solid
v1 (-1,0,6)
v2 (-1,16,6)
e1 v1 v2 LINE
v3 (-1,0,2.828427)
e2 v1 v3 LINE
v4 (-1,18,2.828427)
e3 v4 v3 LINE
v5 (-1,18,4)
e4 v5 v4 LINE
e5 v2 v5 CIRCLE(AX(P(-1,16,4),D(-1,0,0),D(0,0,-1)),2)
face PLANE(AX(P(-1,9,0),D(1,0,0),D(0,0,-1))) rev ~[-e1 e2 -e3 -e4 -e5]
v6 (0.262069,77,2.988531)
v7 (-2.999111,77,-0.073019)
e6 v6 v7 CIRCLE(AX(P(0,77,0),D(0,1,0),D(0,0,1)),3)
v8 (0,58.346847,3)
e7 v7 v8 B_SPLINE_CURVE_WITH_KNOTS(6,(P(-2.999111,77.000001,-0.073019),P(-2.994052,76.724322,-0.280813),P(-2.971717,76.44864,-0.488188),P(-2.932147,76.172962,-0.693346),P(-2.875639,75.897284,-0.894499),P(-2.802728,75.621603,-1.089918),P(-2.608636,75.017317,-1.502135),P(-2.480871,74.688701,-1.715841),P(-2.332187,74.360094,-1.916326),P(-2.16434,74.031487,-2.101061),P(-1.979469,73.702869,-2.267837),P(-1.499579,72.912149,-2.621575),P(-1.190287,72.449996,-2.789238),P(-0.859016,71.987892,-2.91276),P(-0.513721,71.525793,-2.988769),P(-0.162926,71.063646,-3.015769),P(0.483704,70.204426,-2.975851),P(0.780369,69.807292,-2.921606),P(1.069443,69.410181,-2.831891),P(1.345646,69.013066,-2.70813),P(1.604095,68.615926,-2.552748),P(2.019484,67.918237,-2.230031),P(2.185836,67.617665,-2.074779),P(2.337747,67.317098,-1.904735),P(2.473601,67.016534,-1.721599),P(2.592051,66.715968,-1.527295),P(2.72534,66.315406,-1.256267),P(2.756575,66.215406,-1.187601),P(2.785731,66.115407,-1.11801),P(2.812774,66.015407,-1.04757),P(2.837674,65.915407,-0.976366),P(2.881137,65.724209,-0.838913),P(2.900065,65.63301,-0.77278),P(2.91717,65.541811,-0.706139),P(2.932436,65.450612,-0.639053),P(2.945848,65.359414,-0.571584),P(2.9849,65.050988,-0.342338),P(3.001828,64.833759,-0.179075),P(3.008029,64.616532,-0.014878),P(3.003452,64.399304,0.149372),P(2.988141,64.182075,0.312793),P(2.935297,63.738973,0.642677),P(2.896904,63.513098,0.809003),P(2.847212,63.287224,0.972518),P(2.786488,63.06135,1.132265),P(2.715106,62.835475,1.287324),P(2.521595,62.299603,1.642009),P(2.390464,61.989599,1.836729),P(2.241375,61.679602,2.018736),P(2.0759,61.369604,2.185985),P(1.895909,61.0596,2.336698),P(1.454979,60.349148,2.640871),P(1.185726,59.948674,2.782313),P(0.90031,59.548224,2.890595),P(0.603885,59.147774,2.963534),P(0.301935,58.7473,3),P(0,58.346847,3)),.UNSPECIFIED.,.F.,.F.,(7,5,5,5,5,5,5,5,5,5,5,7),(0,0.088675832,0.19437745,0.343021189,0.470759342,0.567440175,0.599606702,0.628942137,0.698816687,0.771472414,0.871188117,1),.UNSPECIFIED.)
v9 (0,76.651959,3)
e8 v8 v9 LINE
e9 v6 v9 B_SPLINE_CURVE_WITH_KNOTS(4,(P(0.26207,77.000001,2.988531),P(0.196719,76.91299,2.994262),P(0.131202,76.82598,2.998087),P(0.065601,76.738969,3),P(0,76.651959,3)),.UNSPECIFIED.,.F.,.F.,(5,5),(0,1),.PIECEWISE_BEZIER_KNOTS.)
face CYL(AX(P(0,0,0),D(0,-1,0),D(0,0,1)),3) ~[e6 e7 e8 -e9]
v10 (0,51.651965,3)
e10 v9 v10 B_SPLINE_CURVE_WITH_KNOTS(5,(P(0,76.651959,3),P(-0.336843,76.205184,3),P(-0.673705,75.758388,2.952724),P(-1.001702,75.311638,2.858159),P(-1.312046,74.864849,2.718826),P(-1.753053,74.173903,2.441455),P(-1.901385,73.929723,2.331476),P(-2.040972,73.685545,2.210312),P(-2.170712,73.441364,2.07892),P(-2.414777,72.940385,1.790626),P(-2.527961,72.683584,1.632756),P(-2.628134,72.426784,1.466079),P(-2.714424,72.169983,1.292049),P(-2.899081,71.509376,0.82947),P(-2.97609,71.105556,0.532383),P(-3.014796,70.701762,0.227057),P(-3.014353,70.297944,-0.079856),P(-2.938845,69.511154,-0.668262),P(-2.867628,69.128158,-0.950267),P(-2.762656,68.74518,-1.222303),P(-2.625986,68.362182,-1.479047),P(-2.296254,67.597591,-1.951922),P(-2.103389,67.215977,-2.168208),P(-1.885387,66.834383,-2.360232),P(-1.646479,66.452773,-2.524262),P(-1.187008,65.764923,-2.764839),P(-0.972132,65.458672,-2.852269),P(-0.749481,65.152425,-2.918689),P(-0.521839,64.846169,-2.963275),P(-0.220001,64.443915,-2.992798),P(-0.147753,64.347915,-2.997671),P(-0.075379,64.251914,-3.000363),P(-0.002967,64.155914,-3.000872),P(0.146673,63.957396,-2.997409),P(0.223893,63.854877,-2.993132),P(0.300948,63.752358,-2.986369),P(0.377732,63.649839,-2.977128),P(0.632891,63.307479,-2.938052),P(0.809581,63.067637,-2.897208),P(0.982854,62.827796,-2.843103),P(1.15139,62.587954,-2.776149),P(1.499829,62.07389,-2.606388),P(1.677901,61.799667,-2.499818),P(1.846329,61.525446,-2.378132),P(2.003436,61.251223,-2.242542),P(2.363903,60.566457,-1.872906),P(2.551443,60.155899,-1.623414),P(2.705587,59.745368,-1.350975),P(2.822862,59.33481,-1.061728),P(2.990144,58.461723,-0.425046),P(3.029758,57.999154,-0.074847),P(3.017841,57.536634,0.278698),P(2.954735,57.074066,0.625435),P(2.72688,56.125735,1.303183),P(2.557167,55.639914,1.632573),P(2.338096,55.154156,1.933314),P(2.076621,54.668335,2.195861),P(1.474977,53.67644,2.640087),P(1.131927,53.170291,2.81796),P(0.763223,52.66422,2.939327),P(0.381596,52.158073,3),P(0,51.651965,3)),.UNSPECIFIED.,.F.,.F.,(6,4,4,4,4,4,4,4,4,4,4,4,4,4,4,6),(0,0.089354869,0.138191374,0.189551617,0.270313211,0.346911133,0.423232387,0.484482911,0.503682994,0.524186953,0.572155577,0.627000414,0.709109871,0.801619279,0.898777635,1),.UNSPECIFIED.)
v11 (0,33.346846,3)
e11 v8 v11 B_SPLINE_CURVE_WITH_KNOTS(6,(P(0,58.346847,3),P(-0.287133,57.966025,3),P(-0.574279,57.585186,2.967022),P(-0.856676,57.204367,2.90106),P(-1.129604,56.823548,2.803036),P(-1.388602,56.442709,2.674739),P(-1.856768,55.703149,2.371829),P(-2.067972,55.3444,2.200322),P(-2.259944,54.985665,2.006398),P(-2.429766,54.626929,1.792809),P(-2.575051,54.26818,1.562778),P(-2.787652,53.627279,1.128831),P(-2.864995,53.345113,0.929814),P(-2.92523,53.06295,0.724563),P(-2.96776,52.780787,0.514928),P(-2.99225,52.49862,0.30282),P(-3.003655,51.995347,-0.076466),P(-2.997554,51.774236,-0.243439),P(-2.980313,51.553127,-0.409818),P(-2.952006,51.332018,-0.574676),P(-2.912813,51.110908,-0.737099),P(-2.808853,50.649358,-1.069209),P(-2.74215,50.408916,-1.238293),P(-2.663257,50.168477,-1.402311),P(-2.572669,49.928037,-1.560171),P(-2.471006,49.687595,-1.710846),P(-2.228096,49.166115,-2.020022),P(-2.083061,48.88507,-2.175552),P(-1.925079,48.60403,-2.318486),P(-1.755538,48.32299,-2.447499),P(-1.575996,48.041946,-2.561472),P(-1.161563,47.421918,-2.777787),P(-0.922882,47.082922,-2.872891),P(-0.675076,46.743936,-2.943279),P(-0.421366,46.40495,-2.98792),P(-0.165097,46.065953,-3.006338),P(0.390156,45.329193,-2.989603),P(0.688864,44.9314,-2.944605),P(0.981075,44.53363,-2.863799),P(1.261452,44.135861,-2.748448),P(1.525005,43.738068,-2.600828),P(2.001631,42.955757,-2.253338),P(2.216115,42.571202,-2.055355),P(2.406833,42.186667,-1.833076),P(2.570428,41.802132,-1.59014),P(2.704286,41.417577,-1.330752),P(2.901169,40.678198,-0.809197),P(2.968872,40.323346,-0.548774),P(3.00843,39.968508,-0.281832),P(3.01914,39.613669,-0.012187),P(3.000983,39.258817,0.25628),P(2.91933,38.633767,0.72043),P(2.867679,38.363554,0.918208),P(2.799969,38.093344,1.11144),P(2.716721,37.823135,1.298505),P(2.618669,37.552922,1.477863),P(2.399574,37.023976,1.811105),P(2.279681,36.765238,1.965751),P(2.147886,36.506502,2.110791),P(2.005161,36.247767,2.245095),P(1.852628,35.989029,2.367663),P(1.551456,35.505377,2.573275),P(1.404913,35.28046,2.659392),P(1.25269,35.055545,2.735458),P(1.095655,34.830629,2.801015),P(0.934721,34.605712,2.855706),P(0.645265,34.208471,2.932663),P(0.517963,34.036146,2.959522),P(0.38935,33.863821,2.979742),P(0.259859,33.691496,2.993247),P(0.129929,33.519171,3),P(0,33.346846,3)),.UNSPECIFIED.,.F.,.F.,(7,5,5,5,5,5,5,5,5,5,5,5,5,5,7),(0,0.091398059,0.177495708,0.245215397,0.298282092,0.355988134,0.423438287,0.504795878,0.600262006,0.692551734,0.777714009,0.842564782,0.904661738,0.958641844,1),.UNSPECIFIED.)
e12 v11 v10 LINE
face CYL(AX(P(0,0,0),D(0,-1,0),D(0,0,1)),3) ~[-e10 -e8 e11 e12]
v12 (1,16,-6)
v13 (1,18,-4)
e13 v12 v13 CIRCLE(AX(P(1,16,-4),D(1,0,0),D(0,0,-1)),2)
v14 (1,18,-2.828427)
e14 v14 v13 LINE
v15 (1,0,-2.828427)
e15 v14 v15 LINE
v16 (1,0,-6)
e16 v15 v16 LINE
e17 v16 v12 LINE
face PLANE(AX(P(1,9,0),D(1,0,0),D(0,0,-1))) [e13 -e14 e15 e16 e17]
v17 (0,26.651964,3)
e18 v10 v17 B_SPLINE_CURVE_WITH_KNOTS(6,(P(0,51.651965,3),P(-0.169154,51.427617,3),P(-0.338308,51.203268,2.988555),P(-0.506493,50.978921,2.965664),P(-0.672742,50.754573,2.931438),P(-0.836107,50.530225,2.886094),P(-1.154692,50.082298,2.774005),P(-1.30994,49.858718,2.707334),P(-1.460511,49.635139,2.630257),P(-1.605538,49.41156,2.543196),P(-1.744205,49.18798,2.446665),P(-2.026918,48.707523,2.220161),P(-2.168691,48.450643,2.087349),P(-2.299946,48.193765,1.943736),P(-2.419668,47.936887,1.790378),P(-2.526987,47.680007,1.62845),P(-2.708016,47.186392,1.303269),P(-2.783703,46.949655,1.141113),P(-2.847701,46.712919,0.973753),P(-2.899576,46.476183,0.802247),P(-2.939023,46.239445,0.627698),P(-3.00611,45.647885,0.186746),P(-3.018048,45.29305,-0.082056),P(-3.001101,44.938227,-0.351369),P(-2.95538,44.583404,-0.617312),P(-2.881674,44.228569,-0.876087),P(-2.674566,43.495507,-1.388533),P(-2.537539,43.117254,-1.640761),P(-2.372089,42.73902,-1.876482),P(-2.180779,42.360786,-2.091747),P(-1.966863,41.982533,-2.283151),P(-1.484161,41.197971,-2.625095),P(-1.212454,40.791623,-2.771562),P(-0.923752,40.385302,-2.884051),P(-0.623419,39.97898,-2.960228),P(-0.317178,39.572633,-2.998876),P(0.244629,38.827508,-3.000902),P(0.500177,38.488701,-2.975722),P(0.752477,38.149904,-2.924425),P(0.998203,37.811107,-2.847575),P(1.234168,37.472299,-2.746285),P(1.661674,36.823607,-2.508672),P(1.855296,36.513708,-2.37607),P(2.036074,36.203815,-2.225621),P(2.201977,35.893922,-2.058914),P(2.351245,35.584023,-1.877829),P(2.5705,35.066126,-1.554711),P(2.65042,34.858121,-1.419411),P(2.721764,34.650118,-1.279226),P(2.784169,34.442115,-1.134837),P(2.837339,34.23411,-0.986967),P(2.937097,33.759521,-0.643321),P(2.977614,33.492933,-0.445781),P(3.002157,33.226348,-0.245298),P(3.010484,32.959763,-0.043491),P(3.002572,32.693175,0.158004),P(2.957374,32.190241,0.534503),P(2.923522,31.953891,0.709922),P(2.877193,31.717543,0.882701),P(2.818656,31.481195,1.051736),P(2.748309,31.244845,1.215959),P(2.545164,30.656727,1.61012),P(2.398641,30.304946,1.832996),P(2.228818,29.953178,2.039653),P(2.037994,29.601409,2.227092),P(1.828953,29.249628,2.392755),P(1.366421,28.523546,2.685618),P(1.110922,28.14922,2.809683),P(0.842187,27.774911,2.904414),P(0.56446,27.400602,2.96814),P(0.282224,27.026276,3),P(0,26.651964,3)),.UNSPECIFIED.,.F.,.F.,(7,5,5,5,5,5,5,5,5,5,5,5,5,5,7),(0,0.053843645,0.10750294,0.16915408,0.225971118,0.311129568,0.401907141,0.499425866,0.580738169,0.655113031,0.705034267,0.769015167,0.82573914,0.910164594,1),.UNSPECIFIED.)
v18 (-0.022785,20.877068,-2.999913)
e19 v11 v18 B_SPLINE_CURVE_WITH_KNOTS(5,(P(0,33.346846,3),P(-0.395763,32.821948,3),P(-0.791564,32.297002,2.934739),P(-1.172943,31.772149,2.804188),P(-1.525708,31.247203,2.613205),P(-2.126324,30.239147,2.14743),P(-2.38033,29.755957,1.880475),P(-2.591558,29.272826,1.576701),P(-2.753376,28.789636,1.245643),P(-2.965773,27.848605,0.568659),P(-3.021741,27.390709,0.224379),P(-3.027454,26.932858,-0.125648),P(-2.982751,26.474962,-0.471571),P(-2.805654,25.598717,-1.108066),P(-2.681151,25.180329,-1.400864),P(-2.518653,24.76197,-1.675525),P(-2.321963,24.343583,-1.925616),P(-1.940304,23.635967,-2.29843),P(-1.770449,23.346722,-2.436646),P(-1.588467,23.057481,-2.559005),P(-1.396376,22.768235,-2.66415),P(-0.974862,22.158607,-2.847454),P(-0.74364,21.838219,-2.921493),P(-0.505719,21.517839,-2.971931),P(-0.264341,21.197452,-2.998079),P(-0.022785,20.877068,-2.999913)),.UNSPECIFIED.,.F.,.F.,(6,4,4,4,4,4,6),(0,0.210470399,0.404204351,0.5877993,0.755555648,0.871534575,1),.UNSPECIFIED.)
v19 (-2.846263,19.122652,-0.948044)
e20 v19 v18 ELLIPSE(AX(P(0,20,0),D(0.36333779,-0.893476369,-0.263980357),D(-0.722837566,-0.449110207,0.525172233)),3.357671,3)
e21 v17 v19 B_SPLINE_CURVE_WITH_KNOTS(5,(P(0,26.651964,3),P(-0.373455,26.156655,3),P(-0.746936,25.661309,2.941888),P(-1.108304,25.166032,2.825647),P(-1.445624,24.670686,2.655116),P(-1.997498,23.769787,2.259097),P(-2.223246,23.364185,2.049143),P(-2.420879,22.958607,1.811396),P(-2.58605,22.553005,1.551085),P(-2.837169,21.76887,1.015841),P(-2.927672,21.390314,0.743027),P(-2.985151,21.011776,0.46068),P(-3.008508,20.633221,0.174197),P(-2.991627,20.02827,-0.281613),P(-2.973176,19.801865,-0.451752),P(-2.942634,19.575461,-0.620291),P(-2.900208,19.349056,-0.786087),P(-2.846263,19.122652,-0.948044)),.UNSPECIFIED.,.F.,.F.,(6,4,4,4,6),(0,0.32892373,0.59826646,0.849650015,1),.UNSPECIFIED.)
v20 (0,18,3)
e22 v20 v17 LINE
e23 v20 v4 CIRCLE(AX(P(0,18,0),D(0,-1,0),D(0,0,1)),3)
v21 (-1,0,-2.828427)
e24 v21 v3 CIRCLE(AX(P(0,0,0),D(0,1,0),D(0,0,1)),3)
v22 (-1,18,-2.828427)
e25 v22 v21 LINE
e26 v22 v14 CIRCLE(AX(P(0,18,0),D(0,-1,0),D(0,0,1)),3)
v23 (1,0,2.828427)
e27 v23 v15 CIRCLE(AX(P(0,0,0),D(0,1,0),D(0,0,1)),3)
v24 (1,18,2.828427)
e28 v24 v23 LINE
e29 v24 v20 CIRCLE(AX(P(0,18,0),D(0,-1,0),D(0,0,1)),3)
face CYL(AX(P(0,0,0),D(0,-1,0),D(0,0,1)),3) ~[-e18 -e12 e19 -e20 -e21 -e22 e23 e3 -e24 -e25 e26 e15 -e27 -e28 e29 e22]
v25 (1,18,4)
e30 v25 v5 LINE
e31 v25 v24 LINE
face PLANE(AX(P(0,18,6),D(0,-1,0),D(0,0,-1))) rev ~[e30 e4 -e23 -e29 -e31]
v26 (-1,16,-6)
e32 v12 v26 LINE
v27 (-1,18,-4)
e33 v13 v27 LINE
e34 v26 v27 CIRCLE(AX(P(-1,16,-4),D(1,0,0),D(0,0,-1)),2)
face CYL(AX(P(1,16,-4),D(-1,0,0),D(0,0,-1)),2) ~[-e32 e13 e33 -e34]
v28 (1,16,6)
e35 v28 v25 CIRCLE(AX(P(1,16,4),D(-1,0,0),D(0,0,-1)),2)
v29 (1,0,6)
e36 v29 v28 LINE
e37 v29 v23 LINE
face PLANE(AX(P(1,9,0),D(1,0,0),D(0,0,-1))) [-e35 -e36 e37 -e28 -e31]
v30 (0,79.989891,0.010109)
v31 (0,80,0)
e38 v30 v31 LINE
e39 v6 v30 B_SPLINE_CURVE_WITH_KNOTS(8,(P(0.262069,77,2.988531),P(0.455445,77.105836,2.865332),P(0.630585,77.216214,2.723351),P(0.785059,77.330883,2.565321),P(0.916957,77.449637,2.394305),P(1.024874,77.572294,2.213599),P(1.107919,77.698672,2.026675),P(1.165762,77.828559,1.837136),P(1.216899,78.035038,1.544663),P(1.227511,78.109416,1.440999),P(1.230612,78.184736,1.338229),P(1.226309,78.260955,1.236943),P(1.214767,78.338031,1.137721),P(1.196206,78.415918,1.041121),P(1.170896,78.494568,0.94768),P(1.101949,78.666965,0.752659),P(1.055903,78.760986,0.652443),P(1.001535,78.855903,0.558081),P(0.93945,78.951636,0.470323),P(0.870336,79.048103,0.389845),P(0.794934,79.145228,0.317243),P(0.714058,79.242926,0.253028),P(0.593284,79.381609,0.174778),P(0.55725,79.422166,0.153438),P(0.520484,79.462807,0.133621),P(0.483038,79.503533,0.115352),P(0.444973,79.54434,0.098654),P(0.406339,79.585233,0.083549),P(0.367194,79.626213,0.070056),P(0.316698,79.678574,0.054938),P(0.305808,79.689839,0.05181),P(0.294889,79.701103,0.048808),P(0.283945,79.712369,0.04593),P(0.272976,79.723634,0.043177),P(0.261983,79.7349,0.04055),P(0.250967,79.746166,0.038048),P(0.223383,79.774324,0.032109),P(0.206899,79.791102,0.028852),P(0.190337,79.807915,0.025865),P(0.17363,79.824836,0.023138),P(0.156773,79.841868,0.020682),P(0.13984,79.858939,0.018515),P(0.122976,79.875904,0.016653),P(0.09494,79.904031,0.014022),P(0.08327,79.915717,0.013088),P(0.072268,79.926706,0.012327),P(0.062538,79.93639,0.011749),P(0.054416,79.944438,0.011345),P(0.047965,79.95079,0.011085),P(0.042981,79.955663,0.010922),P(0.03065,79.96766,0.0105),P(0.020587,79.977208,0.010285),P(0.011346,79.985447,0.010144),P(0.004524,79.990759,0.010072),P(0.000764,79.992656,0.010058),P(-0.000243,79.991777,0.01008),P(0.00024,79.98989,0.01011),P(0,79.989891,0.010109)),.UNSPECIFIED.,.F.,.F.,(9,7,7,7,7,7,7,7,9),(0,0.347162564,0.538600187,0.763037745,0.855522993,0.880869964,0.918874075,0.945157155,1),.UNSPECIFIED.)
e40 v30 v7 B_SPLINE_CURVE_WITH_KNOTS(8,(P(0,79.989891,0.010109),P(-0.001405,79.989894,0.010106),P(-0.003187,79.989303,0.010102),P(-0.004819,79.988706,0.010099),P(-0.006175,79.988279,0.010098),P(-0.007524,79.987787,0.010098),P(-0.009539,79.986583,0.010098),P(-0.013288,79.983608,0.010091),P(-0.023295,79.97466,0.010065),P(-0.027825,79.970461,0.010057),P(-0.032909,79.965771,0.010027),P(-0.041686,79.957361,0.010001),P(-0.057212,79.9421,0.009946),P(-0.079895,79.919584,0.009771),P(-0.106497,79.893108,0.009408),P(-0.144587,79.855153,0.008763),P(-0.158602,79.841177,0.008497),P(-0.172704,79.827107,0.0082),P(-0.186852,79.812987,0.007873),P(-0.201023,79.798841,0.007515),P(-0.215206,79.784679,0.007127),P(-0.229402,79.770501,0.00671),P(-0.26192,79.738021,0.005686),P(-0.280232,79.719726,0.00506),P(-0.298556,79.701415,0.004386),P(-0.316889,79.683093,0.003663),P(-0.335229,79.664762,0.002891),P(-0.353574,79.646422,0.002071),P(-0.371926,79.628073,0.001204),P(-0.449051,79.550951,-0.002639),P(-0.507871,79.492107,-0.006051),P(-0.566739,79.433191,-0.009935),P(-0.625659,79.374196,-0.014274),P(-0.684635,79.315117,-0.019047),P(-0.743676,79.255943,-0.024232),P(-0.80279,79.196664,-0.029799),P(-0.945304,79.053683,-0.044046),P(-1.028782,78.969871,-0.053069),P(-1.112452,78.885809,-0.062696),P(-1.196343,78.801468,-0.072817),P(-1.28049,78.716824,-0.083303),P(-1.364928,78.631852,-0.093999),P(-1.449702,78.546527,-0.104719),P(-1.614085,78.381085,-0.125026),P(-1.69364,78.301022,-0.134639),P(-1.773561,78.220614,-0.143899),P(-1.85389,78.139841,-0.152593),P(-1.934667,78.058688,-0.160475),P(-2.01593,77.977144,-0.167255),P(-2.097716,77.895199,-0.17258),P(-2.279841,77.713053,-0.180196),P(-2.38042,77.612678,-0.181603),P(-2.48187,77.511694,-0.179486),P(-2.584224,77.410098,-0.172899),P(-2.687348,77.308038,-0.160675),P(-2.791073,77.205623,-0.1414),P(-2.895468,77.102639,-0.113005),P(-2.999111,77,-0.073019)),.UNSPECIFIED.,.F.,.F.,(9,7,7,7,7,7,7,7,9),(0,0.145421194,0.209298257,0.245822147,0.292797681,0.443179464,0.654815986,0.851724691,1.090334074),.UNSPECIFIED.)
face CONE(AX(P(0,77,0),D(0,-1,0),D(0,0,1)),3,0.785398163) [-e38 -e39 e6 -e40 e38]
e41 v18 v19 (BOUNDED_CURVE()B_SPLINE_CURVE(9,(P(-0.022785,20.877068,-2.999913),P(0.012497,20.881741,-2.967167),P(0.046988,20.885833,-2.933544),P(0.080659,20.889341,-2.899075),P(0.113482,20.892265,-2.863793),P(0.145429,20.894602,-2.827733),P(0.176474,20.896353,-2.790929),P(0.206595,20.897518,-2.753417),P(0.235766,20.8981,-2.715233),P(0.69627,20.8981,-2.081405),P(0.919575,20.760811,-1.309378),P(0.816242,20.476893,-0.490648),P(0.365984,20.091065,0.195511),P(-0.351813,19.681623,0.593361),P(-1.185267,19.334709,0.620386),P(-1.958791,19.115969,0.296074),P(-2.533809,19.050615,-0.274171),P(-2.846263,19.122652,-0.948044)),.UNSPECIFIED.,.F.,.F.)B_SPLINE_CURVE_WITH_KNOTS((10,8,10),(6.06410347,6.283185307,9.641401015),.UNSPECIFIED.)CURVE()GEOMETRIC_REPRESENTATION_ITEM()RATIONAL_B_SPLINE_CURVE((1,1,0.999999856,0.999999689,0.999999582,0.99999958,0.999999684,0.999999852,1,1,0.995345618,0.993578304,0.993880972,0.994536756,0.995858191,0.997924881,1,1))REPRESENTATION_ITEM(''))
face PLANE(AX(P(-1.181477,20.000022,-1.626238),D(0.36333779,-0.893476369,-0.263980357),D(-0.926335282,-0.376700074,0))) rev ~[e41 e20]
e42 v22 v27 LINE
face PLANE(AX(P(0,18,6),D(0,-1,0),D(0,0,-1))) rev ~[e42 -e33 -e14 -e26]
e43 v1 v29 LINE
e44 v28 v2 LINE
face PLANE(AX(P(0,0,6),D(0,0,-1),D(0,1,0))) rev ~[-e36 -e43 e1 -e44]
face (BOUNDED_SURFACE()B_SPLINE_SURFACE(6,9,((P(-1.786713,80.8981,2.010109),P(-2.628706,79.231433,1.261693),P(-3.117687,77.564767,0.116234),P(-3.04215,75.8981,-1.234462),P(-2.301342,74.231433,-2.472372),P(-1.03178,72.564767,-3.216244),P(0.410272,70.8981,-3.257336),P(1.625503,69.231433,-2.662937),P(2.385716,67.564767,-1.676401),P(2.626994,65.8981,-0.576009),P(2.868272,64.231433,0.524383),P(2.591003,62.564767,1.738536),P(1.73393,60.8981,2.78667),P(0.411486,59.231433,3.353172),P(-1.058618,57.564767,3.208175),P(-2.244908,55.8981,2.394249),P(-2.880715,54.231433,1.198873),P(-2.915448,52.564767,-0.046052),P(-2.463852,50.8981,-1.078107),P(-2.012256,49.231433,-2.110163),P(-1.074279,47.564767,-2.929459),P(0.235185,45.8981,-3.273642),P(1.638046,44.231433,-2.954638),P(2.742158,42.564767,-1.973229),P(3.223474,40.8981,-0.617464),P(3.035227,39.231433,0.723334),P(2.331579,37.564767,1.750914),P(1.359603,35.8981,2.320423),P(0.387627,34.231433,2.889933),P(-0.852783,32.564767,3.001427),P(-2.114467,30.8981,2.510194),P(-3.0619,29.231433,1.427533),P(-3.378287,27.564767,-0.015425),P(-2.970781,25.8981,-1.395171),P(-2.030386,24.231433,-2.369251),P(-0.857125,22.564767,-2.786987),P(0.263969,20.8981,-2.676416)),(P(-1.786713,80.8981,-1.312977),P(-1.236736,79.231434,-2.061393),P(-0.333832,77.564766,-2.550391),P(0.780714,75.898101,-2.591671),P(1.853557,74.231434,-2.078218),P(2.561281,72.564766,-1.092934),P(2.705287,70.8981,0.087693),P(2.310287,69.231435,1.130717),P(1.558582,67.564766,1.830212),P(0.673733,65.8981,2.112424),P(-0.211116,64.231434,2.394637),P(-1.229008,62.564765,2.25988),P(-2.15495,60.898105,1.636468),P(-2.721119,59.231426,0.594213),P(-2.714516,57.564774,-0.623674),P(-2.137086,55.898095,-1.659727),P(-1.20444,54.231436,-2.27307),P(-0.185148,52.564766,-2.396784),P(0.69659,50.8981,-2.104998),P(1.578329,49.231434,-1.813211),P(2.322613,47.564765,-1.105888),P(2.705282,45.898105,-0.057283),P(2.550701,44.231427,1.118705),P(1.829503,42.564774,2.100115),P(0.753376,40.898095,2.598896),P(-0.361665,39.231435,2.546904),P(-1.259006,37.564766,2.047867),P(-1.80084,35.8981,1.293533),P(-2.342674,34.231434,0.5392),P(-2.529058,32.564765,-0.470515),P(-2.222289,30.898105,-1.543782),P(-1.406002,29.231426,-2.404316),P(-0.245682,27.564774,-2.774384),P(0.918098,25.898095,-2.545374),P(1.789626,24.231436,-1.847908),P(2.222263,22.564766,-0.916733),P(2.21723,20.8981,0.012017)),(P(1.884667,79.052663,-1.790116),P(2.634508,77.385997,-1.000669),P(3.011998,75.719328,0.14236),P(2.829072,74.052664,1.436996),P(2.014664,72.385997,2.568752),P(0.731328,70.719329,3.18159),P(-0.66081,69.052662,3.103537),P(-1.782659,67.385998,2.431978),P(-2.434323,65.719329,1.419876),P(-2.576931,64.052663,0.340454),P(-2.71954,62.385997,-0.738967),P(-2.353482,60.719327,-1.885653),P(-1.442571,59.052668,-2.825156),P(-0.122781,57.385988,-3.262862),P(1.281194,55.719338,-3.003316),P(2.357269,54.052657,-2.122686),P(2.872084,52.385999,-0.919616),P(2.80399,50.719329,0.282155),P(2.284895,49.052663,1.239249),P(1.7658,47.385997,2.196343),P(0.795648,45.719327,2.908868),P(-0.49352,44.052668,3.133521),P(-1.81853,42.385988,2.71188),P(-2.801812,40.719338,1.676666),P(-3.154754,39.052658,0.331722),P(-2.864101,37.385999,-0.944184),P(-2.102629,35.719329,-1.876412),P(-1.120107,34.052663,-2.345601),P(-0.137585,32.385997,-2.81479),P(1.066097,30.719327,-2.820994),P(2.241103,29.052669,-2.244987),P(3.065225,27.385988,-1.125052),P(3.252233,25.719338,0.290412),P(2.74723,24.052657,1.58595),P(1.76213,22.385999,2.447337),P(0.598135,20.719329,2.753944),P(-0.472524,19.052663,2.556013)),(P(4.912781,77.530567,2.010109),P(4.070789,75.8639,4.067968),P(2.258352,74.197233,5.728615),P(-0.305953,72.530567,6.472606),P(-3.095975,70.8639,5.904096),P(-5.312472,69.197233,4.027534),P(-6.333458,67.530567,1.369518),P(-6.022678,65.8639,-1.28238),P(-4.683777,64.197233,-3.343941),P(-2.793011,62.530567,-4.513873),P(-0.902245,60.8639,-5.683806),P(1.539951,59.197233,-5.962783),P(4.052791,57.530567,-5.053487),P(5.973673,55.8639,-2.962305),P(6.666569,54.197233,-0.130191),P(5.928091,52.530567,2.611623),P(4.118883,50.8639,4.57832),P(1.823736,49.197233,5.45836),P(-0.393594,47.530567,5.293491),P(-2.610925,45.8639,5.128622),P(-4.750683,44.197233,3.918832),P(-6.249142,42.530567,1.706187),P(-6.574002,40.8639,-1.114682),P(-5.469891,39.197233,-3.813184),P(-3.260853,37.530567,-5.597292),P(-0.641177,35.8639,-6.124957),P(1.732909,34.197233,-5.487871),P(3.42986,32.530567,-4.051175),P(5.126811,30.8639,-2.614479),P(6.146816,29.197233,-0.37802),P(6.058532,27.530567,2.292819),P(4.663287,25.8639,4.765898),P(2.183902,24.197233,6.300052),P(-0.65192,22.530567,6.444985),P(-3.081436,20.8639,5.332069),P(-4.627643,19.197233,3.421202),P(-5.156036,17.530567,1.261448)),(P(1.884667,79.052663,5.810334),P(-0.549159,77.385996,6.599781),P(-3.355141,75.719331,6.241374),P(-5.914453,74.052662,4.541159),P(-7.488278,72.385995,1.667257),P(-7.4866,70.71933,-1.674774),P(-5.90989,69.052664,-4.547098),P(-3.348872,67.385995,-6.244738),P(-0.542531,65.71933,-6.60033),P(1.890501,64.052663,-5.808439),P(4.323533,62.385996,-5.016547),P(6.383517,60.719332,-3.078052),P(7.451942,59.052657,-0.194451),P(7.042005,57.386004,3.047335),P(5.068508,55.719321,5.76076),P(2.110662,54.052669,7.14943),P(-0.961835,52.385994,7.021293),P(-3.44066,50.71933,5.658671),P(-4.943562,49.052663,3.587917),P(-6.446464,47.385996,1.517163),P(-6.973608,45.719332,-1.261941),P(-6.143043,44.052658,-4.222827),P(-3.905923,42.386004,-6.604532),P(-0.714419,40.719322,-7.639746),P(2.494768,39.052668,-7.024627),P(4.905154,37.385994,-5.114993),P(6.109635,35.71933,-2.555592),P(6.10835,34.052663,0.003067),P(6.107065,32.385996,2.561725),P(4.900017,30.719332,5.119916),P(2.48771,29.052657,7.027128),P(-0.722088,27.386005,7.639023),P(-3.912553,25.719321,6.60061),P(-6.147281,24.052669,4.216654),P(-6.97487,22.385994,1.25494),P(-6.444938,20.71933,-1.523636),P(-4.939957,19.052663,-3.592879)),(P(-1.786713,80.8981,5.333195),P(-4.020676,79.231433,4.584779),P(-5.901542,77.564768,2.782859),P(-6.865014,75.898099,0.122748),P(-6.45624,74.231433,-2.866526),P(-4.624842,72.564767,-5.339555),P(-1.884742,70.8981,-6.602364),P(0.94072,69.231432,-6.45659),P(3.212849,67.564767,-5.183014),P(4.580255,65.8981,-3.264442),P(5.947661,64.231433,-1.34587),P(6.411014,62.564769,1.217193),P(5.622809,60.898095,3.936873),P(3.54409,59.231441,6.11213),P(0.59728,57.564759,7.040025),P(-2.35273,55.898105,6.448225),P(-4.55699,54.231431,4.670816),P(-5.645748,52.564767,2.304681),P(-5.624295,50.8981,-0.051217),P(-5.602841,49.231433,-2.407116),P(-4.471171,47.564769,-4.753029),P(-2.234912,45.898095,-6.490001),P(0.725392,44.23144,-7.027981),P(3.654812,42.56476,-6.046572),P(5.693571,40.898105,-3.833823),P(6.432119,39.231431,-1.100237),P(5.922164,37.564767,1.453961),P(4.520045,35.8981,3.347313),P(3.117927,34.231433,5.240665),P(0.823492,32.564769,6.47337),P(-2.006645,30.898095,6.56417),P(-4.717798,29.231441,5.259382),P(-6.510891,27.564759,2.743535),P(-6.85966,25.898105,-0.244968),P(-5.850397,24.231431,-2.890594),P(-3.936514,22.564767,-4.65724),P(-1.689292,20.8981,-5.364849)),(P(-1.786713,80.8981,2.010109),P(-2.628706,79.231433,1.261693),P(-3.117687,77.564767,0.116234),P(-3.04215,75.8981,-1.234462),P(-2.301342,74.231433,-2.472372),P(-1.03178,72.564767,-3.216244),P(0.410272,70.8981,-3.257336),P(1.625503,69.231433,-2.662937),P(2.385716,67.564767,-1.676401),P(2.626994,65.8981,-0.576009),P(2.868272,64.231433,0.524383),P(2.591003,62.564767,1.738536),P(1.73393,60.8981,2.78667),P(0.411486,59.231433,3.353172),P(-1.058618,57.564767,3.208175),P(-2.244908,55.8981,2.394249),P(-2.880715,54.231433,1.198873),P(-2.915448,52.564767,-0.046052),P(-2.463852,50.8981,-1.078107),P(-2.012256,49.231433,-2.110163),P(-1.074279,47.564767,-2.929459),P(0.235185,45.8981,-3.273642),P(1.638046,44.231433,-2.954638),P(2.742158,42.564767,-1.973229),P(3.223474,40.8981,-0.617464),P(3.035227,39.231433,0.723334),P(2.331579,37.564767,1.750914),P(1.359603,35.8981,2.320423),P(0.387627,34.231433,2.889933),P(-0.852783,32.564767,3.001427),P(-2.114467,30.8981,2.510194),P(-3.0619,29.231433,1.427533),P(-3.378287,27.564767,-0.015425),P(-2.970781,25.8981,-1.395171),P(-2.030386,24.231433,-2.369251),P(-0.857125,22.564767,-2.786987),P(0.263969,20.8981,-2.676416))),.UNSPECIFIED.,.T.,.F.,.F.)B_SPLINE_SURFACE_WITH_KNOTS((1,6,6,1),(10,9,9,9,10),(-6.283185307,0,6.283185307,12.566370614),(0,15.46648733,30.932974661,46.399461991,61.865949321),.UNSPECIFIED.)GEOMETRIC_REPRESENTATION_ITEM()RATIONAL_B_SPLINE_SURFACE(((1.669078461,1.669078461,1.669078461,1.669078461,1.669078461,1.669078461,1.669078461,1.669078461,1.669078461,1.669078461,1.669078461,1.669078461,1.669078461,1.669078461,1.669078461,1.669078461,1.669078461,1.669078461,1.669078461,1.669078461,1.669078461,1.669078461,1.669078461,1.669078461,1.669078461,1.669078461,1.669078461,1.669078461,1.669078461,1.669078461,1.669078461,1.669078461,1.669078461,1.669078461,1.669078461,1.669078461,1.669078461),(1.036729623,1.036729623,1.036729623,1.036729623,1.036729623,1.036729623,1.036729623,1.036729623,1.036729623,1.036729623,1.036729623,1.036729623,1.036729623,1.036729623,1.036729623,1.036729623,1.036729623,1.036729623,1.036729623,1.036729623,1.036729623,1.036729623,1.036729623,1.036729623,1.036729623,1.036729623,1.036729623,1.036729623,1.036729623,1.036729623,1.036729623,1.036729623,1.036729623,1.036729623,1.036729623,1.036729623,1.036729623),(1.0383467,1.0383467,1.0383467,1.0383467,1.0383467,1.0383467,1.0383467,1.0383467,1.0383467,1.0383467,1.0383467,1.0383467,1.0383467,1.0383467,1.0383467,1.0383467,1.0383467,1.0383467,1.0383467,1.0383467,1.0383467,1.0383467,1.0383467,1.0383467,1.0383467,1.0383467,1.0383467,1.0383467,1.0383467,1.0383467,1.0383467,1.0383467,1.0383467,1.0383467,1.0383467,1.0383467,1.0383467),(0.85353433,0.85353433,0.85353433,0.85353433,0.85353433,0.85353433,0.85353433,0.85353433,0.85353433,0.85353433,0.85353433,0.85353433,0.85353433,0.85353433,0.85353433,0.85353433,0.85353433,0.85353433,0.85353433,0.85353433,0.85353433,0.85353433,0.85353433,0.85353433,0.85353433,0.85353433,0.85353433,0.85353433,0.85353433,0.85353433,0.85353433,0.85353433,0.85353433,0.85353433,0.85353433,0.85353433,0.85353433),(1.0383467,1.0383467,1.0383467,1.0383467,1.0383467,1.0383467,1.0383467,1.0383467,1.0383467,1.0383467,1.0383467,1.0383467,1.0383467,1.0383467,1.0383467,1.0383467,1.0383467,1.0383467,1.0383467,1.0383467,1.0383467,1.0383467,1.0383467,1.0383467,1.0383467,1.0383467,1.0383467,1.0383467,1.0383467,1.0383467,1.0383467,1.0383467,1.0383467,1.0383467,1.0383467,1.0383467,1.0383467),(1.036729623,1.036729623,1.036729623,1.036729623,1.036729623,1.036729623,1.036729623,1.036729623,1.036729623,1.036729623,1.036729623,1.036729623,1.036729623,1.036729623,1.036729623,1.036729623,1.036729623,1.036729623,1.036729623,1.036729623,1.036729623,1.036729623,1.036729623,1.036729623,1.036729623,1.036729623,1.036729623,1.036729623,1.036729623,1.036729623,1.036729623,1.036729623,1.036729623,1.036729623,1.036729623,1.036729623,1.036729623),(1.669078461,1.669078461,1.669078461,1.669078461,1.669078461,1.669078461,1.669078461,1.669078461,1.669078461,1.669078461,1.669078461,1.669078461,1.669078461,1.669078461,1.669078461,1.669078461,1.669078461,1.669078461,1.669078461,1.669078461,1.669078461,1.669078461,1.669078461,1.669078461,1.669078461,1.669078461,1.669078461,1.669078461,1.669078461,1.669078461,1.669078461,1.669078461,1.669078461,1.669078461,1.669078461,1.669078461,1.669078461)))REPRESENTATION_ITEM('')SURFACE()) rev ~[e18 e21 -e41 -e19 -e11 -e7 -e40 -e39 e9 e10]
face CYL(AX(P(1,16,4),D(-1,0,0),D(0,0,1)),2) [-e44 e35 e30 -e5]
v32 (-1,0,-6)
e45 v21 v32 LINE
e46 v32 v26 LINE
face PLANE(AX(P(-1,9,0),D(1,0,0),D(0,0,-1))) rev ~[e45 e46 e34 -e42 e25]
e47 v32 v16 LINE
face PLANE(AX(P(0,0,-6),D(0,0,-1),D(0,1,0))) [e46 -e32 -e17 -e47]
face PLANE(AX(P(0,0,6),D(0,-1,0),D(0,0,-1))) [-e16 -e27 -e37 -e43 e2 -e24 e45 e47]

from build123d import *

# Parameters (mm, degrees)
BODY_PROFILE_6_R          = 3
DRILL_BODY_6_X_80_DEPTH   = 80
TIP_CHAMFER_3X45_SIZE     = 3
HELICAL_FLUTE_PITCH       = 25
HELICAL_FLUTE_HEIGHT      = 60
HELICAL_FLUTE_RADIUS      = 2
HELICAL_FLUTE_START_ANGLE = 180
FLUTE_PROFILE_4_R         = 2
TANG_PROFILE_12X18_W      = 12
TANG_PROFILE_12X18_H      = 18
DRIVE_TANG_2MM_DEPTH      = 1
TANG_FILLET_R2_A_R        = 2
TANG_FILLET_R2_B_R        = 2


with BuildPart() as part:
    # Body Profile Ø6 → Drill Body Ø6 x 80 (new body)
    with BuildSketch(Plane(origin=(0, 0, 0), x_dir=(1, 0, 0), z_dir=(0, 1, 0))):
        with Locations(Location((0, 0, 0), (0, 0, 270))):
            Circle(BODY_PROFILE_6_R)
    extrude(amount=DRILL_BODY_6_X_80_DEPTH)

    # Tip Chamfer 3x45°
    tip_chamfer_3x45_edges = [part.edges().sort_by_distance(p)[0] for p in [
        (0, 80, -3),
    ]]
    chamfer(tip_chamfer_3x45_edges, length=TIP_CHAMFER_3X45_SIZE)

    # Helical Flute: sweep along a helix
    with BuildLine() as helical_flute_path:
        add(Helix(HELICAL_FLUTE_PITCH, HELICAL_FLUTE_HEIGHT, HELICAL_FLUTE_RADIUS, center=(0, 80, 0), direction=(0, -1, 0), mode=Mode.PRIVATE).rotate(Axis((0, 80, 0), (0, -1, 0)), HELICAL_FLUTE_START_ANGLE))
    # Flute Profile Ø4 → Helical Flute (sweep, cut)
    with BuildSketch(Plane(origin=(0, 80, 2), x_dir=(-0.8934763687940476, 0.4491102074175148, -3.3349691128186272e-15), z_dir=(-0.44911020741751484, -0.8934763687940477, 6.634710242048462e-15))):
        with Locations((-0.000268006, -0.010109249)):
            Circle(FLUTE_PROFILE_4_R)
    sweep(path=helical_flute_path.line, is_frenet=True, mode=Mode.SUBTRACT)

    # Tang Profile 12x18 → Drive Tang 2mm (add, symmetric)
    with BuildSketch(Plane(origin=(0, 0, 0), x_dir=(0, 0, -1), z_dir=(1, 0, 0))):
        with Locations((0, 9)):
            Rectangle(TANG_PROFILE_12X18_W, TANG_PROFILE_12X18_H)
    extrude(amount=DRIVE_TANG_2MM_DEPTH, both=True)

    # Tang Fillet R2 A
    tang_fillet_r2_a_edges = [part.edges().sort_by_distance(p)[0] for p in [
        (0, 18, 6),
    ]]
    fillet(tang_fillet_r2_a_edges, radius=TANG_FILLET_R2_A_R)

    # Tang Fillet R2 B
    tang_fillet_r2_b_edges = [part.edges().sort_by_distance(p)[0] for p in [
        (0, 18, -6),
    ]]
    fillet(tang_fillet_r2_b_edges, radius=TANG_FILLET_R2_B_R)


solid = part.part
